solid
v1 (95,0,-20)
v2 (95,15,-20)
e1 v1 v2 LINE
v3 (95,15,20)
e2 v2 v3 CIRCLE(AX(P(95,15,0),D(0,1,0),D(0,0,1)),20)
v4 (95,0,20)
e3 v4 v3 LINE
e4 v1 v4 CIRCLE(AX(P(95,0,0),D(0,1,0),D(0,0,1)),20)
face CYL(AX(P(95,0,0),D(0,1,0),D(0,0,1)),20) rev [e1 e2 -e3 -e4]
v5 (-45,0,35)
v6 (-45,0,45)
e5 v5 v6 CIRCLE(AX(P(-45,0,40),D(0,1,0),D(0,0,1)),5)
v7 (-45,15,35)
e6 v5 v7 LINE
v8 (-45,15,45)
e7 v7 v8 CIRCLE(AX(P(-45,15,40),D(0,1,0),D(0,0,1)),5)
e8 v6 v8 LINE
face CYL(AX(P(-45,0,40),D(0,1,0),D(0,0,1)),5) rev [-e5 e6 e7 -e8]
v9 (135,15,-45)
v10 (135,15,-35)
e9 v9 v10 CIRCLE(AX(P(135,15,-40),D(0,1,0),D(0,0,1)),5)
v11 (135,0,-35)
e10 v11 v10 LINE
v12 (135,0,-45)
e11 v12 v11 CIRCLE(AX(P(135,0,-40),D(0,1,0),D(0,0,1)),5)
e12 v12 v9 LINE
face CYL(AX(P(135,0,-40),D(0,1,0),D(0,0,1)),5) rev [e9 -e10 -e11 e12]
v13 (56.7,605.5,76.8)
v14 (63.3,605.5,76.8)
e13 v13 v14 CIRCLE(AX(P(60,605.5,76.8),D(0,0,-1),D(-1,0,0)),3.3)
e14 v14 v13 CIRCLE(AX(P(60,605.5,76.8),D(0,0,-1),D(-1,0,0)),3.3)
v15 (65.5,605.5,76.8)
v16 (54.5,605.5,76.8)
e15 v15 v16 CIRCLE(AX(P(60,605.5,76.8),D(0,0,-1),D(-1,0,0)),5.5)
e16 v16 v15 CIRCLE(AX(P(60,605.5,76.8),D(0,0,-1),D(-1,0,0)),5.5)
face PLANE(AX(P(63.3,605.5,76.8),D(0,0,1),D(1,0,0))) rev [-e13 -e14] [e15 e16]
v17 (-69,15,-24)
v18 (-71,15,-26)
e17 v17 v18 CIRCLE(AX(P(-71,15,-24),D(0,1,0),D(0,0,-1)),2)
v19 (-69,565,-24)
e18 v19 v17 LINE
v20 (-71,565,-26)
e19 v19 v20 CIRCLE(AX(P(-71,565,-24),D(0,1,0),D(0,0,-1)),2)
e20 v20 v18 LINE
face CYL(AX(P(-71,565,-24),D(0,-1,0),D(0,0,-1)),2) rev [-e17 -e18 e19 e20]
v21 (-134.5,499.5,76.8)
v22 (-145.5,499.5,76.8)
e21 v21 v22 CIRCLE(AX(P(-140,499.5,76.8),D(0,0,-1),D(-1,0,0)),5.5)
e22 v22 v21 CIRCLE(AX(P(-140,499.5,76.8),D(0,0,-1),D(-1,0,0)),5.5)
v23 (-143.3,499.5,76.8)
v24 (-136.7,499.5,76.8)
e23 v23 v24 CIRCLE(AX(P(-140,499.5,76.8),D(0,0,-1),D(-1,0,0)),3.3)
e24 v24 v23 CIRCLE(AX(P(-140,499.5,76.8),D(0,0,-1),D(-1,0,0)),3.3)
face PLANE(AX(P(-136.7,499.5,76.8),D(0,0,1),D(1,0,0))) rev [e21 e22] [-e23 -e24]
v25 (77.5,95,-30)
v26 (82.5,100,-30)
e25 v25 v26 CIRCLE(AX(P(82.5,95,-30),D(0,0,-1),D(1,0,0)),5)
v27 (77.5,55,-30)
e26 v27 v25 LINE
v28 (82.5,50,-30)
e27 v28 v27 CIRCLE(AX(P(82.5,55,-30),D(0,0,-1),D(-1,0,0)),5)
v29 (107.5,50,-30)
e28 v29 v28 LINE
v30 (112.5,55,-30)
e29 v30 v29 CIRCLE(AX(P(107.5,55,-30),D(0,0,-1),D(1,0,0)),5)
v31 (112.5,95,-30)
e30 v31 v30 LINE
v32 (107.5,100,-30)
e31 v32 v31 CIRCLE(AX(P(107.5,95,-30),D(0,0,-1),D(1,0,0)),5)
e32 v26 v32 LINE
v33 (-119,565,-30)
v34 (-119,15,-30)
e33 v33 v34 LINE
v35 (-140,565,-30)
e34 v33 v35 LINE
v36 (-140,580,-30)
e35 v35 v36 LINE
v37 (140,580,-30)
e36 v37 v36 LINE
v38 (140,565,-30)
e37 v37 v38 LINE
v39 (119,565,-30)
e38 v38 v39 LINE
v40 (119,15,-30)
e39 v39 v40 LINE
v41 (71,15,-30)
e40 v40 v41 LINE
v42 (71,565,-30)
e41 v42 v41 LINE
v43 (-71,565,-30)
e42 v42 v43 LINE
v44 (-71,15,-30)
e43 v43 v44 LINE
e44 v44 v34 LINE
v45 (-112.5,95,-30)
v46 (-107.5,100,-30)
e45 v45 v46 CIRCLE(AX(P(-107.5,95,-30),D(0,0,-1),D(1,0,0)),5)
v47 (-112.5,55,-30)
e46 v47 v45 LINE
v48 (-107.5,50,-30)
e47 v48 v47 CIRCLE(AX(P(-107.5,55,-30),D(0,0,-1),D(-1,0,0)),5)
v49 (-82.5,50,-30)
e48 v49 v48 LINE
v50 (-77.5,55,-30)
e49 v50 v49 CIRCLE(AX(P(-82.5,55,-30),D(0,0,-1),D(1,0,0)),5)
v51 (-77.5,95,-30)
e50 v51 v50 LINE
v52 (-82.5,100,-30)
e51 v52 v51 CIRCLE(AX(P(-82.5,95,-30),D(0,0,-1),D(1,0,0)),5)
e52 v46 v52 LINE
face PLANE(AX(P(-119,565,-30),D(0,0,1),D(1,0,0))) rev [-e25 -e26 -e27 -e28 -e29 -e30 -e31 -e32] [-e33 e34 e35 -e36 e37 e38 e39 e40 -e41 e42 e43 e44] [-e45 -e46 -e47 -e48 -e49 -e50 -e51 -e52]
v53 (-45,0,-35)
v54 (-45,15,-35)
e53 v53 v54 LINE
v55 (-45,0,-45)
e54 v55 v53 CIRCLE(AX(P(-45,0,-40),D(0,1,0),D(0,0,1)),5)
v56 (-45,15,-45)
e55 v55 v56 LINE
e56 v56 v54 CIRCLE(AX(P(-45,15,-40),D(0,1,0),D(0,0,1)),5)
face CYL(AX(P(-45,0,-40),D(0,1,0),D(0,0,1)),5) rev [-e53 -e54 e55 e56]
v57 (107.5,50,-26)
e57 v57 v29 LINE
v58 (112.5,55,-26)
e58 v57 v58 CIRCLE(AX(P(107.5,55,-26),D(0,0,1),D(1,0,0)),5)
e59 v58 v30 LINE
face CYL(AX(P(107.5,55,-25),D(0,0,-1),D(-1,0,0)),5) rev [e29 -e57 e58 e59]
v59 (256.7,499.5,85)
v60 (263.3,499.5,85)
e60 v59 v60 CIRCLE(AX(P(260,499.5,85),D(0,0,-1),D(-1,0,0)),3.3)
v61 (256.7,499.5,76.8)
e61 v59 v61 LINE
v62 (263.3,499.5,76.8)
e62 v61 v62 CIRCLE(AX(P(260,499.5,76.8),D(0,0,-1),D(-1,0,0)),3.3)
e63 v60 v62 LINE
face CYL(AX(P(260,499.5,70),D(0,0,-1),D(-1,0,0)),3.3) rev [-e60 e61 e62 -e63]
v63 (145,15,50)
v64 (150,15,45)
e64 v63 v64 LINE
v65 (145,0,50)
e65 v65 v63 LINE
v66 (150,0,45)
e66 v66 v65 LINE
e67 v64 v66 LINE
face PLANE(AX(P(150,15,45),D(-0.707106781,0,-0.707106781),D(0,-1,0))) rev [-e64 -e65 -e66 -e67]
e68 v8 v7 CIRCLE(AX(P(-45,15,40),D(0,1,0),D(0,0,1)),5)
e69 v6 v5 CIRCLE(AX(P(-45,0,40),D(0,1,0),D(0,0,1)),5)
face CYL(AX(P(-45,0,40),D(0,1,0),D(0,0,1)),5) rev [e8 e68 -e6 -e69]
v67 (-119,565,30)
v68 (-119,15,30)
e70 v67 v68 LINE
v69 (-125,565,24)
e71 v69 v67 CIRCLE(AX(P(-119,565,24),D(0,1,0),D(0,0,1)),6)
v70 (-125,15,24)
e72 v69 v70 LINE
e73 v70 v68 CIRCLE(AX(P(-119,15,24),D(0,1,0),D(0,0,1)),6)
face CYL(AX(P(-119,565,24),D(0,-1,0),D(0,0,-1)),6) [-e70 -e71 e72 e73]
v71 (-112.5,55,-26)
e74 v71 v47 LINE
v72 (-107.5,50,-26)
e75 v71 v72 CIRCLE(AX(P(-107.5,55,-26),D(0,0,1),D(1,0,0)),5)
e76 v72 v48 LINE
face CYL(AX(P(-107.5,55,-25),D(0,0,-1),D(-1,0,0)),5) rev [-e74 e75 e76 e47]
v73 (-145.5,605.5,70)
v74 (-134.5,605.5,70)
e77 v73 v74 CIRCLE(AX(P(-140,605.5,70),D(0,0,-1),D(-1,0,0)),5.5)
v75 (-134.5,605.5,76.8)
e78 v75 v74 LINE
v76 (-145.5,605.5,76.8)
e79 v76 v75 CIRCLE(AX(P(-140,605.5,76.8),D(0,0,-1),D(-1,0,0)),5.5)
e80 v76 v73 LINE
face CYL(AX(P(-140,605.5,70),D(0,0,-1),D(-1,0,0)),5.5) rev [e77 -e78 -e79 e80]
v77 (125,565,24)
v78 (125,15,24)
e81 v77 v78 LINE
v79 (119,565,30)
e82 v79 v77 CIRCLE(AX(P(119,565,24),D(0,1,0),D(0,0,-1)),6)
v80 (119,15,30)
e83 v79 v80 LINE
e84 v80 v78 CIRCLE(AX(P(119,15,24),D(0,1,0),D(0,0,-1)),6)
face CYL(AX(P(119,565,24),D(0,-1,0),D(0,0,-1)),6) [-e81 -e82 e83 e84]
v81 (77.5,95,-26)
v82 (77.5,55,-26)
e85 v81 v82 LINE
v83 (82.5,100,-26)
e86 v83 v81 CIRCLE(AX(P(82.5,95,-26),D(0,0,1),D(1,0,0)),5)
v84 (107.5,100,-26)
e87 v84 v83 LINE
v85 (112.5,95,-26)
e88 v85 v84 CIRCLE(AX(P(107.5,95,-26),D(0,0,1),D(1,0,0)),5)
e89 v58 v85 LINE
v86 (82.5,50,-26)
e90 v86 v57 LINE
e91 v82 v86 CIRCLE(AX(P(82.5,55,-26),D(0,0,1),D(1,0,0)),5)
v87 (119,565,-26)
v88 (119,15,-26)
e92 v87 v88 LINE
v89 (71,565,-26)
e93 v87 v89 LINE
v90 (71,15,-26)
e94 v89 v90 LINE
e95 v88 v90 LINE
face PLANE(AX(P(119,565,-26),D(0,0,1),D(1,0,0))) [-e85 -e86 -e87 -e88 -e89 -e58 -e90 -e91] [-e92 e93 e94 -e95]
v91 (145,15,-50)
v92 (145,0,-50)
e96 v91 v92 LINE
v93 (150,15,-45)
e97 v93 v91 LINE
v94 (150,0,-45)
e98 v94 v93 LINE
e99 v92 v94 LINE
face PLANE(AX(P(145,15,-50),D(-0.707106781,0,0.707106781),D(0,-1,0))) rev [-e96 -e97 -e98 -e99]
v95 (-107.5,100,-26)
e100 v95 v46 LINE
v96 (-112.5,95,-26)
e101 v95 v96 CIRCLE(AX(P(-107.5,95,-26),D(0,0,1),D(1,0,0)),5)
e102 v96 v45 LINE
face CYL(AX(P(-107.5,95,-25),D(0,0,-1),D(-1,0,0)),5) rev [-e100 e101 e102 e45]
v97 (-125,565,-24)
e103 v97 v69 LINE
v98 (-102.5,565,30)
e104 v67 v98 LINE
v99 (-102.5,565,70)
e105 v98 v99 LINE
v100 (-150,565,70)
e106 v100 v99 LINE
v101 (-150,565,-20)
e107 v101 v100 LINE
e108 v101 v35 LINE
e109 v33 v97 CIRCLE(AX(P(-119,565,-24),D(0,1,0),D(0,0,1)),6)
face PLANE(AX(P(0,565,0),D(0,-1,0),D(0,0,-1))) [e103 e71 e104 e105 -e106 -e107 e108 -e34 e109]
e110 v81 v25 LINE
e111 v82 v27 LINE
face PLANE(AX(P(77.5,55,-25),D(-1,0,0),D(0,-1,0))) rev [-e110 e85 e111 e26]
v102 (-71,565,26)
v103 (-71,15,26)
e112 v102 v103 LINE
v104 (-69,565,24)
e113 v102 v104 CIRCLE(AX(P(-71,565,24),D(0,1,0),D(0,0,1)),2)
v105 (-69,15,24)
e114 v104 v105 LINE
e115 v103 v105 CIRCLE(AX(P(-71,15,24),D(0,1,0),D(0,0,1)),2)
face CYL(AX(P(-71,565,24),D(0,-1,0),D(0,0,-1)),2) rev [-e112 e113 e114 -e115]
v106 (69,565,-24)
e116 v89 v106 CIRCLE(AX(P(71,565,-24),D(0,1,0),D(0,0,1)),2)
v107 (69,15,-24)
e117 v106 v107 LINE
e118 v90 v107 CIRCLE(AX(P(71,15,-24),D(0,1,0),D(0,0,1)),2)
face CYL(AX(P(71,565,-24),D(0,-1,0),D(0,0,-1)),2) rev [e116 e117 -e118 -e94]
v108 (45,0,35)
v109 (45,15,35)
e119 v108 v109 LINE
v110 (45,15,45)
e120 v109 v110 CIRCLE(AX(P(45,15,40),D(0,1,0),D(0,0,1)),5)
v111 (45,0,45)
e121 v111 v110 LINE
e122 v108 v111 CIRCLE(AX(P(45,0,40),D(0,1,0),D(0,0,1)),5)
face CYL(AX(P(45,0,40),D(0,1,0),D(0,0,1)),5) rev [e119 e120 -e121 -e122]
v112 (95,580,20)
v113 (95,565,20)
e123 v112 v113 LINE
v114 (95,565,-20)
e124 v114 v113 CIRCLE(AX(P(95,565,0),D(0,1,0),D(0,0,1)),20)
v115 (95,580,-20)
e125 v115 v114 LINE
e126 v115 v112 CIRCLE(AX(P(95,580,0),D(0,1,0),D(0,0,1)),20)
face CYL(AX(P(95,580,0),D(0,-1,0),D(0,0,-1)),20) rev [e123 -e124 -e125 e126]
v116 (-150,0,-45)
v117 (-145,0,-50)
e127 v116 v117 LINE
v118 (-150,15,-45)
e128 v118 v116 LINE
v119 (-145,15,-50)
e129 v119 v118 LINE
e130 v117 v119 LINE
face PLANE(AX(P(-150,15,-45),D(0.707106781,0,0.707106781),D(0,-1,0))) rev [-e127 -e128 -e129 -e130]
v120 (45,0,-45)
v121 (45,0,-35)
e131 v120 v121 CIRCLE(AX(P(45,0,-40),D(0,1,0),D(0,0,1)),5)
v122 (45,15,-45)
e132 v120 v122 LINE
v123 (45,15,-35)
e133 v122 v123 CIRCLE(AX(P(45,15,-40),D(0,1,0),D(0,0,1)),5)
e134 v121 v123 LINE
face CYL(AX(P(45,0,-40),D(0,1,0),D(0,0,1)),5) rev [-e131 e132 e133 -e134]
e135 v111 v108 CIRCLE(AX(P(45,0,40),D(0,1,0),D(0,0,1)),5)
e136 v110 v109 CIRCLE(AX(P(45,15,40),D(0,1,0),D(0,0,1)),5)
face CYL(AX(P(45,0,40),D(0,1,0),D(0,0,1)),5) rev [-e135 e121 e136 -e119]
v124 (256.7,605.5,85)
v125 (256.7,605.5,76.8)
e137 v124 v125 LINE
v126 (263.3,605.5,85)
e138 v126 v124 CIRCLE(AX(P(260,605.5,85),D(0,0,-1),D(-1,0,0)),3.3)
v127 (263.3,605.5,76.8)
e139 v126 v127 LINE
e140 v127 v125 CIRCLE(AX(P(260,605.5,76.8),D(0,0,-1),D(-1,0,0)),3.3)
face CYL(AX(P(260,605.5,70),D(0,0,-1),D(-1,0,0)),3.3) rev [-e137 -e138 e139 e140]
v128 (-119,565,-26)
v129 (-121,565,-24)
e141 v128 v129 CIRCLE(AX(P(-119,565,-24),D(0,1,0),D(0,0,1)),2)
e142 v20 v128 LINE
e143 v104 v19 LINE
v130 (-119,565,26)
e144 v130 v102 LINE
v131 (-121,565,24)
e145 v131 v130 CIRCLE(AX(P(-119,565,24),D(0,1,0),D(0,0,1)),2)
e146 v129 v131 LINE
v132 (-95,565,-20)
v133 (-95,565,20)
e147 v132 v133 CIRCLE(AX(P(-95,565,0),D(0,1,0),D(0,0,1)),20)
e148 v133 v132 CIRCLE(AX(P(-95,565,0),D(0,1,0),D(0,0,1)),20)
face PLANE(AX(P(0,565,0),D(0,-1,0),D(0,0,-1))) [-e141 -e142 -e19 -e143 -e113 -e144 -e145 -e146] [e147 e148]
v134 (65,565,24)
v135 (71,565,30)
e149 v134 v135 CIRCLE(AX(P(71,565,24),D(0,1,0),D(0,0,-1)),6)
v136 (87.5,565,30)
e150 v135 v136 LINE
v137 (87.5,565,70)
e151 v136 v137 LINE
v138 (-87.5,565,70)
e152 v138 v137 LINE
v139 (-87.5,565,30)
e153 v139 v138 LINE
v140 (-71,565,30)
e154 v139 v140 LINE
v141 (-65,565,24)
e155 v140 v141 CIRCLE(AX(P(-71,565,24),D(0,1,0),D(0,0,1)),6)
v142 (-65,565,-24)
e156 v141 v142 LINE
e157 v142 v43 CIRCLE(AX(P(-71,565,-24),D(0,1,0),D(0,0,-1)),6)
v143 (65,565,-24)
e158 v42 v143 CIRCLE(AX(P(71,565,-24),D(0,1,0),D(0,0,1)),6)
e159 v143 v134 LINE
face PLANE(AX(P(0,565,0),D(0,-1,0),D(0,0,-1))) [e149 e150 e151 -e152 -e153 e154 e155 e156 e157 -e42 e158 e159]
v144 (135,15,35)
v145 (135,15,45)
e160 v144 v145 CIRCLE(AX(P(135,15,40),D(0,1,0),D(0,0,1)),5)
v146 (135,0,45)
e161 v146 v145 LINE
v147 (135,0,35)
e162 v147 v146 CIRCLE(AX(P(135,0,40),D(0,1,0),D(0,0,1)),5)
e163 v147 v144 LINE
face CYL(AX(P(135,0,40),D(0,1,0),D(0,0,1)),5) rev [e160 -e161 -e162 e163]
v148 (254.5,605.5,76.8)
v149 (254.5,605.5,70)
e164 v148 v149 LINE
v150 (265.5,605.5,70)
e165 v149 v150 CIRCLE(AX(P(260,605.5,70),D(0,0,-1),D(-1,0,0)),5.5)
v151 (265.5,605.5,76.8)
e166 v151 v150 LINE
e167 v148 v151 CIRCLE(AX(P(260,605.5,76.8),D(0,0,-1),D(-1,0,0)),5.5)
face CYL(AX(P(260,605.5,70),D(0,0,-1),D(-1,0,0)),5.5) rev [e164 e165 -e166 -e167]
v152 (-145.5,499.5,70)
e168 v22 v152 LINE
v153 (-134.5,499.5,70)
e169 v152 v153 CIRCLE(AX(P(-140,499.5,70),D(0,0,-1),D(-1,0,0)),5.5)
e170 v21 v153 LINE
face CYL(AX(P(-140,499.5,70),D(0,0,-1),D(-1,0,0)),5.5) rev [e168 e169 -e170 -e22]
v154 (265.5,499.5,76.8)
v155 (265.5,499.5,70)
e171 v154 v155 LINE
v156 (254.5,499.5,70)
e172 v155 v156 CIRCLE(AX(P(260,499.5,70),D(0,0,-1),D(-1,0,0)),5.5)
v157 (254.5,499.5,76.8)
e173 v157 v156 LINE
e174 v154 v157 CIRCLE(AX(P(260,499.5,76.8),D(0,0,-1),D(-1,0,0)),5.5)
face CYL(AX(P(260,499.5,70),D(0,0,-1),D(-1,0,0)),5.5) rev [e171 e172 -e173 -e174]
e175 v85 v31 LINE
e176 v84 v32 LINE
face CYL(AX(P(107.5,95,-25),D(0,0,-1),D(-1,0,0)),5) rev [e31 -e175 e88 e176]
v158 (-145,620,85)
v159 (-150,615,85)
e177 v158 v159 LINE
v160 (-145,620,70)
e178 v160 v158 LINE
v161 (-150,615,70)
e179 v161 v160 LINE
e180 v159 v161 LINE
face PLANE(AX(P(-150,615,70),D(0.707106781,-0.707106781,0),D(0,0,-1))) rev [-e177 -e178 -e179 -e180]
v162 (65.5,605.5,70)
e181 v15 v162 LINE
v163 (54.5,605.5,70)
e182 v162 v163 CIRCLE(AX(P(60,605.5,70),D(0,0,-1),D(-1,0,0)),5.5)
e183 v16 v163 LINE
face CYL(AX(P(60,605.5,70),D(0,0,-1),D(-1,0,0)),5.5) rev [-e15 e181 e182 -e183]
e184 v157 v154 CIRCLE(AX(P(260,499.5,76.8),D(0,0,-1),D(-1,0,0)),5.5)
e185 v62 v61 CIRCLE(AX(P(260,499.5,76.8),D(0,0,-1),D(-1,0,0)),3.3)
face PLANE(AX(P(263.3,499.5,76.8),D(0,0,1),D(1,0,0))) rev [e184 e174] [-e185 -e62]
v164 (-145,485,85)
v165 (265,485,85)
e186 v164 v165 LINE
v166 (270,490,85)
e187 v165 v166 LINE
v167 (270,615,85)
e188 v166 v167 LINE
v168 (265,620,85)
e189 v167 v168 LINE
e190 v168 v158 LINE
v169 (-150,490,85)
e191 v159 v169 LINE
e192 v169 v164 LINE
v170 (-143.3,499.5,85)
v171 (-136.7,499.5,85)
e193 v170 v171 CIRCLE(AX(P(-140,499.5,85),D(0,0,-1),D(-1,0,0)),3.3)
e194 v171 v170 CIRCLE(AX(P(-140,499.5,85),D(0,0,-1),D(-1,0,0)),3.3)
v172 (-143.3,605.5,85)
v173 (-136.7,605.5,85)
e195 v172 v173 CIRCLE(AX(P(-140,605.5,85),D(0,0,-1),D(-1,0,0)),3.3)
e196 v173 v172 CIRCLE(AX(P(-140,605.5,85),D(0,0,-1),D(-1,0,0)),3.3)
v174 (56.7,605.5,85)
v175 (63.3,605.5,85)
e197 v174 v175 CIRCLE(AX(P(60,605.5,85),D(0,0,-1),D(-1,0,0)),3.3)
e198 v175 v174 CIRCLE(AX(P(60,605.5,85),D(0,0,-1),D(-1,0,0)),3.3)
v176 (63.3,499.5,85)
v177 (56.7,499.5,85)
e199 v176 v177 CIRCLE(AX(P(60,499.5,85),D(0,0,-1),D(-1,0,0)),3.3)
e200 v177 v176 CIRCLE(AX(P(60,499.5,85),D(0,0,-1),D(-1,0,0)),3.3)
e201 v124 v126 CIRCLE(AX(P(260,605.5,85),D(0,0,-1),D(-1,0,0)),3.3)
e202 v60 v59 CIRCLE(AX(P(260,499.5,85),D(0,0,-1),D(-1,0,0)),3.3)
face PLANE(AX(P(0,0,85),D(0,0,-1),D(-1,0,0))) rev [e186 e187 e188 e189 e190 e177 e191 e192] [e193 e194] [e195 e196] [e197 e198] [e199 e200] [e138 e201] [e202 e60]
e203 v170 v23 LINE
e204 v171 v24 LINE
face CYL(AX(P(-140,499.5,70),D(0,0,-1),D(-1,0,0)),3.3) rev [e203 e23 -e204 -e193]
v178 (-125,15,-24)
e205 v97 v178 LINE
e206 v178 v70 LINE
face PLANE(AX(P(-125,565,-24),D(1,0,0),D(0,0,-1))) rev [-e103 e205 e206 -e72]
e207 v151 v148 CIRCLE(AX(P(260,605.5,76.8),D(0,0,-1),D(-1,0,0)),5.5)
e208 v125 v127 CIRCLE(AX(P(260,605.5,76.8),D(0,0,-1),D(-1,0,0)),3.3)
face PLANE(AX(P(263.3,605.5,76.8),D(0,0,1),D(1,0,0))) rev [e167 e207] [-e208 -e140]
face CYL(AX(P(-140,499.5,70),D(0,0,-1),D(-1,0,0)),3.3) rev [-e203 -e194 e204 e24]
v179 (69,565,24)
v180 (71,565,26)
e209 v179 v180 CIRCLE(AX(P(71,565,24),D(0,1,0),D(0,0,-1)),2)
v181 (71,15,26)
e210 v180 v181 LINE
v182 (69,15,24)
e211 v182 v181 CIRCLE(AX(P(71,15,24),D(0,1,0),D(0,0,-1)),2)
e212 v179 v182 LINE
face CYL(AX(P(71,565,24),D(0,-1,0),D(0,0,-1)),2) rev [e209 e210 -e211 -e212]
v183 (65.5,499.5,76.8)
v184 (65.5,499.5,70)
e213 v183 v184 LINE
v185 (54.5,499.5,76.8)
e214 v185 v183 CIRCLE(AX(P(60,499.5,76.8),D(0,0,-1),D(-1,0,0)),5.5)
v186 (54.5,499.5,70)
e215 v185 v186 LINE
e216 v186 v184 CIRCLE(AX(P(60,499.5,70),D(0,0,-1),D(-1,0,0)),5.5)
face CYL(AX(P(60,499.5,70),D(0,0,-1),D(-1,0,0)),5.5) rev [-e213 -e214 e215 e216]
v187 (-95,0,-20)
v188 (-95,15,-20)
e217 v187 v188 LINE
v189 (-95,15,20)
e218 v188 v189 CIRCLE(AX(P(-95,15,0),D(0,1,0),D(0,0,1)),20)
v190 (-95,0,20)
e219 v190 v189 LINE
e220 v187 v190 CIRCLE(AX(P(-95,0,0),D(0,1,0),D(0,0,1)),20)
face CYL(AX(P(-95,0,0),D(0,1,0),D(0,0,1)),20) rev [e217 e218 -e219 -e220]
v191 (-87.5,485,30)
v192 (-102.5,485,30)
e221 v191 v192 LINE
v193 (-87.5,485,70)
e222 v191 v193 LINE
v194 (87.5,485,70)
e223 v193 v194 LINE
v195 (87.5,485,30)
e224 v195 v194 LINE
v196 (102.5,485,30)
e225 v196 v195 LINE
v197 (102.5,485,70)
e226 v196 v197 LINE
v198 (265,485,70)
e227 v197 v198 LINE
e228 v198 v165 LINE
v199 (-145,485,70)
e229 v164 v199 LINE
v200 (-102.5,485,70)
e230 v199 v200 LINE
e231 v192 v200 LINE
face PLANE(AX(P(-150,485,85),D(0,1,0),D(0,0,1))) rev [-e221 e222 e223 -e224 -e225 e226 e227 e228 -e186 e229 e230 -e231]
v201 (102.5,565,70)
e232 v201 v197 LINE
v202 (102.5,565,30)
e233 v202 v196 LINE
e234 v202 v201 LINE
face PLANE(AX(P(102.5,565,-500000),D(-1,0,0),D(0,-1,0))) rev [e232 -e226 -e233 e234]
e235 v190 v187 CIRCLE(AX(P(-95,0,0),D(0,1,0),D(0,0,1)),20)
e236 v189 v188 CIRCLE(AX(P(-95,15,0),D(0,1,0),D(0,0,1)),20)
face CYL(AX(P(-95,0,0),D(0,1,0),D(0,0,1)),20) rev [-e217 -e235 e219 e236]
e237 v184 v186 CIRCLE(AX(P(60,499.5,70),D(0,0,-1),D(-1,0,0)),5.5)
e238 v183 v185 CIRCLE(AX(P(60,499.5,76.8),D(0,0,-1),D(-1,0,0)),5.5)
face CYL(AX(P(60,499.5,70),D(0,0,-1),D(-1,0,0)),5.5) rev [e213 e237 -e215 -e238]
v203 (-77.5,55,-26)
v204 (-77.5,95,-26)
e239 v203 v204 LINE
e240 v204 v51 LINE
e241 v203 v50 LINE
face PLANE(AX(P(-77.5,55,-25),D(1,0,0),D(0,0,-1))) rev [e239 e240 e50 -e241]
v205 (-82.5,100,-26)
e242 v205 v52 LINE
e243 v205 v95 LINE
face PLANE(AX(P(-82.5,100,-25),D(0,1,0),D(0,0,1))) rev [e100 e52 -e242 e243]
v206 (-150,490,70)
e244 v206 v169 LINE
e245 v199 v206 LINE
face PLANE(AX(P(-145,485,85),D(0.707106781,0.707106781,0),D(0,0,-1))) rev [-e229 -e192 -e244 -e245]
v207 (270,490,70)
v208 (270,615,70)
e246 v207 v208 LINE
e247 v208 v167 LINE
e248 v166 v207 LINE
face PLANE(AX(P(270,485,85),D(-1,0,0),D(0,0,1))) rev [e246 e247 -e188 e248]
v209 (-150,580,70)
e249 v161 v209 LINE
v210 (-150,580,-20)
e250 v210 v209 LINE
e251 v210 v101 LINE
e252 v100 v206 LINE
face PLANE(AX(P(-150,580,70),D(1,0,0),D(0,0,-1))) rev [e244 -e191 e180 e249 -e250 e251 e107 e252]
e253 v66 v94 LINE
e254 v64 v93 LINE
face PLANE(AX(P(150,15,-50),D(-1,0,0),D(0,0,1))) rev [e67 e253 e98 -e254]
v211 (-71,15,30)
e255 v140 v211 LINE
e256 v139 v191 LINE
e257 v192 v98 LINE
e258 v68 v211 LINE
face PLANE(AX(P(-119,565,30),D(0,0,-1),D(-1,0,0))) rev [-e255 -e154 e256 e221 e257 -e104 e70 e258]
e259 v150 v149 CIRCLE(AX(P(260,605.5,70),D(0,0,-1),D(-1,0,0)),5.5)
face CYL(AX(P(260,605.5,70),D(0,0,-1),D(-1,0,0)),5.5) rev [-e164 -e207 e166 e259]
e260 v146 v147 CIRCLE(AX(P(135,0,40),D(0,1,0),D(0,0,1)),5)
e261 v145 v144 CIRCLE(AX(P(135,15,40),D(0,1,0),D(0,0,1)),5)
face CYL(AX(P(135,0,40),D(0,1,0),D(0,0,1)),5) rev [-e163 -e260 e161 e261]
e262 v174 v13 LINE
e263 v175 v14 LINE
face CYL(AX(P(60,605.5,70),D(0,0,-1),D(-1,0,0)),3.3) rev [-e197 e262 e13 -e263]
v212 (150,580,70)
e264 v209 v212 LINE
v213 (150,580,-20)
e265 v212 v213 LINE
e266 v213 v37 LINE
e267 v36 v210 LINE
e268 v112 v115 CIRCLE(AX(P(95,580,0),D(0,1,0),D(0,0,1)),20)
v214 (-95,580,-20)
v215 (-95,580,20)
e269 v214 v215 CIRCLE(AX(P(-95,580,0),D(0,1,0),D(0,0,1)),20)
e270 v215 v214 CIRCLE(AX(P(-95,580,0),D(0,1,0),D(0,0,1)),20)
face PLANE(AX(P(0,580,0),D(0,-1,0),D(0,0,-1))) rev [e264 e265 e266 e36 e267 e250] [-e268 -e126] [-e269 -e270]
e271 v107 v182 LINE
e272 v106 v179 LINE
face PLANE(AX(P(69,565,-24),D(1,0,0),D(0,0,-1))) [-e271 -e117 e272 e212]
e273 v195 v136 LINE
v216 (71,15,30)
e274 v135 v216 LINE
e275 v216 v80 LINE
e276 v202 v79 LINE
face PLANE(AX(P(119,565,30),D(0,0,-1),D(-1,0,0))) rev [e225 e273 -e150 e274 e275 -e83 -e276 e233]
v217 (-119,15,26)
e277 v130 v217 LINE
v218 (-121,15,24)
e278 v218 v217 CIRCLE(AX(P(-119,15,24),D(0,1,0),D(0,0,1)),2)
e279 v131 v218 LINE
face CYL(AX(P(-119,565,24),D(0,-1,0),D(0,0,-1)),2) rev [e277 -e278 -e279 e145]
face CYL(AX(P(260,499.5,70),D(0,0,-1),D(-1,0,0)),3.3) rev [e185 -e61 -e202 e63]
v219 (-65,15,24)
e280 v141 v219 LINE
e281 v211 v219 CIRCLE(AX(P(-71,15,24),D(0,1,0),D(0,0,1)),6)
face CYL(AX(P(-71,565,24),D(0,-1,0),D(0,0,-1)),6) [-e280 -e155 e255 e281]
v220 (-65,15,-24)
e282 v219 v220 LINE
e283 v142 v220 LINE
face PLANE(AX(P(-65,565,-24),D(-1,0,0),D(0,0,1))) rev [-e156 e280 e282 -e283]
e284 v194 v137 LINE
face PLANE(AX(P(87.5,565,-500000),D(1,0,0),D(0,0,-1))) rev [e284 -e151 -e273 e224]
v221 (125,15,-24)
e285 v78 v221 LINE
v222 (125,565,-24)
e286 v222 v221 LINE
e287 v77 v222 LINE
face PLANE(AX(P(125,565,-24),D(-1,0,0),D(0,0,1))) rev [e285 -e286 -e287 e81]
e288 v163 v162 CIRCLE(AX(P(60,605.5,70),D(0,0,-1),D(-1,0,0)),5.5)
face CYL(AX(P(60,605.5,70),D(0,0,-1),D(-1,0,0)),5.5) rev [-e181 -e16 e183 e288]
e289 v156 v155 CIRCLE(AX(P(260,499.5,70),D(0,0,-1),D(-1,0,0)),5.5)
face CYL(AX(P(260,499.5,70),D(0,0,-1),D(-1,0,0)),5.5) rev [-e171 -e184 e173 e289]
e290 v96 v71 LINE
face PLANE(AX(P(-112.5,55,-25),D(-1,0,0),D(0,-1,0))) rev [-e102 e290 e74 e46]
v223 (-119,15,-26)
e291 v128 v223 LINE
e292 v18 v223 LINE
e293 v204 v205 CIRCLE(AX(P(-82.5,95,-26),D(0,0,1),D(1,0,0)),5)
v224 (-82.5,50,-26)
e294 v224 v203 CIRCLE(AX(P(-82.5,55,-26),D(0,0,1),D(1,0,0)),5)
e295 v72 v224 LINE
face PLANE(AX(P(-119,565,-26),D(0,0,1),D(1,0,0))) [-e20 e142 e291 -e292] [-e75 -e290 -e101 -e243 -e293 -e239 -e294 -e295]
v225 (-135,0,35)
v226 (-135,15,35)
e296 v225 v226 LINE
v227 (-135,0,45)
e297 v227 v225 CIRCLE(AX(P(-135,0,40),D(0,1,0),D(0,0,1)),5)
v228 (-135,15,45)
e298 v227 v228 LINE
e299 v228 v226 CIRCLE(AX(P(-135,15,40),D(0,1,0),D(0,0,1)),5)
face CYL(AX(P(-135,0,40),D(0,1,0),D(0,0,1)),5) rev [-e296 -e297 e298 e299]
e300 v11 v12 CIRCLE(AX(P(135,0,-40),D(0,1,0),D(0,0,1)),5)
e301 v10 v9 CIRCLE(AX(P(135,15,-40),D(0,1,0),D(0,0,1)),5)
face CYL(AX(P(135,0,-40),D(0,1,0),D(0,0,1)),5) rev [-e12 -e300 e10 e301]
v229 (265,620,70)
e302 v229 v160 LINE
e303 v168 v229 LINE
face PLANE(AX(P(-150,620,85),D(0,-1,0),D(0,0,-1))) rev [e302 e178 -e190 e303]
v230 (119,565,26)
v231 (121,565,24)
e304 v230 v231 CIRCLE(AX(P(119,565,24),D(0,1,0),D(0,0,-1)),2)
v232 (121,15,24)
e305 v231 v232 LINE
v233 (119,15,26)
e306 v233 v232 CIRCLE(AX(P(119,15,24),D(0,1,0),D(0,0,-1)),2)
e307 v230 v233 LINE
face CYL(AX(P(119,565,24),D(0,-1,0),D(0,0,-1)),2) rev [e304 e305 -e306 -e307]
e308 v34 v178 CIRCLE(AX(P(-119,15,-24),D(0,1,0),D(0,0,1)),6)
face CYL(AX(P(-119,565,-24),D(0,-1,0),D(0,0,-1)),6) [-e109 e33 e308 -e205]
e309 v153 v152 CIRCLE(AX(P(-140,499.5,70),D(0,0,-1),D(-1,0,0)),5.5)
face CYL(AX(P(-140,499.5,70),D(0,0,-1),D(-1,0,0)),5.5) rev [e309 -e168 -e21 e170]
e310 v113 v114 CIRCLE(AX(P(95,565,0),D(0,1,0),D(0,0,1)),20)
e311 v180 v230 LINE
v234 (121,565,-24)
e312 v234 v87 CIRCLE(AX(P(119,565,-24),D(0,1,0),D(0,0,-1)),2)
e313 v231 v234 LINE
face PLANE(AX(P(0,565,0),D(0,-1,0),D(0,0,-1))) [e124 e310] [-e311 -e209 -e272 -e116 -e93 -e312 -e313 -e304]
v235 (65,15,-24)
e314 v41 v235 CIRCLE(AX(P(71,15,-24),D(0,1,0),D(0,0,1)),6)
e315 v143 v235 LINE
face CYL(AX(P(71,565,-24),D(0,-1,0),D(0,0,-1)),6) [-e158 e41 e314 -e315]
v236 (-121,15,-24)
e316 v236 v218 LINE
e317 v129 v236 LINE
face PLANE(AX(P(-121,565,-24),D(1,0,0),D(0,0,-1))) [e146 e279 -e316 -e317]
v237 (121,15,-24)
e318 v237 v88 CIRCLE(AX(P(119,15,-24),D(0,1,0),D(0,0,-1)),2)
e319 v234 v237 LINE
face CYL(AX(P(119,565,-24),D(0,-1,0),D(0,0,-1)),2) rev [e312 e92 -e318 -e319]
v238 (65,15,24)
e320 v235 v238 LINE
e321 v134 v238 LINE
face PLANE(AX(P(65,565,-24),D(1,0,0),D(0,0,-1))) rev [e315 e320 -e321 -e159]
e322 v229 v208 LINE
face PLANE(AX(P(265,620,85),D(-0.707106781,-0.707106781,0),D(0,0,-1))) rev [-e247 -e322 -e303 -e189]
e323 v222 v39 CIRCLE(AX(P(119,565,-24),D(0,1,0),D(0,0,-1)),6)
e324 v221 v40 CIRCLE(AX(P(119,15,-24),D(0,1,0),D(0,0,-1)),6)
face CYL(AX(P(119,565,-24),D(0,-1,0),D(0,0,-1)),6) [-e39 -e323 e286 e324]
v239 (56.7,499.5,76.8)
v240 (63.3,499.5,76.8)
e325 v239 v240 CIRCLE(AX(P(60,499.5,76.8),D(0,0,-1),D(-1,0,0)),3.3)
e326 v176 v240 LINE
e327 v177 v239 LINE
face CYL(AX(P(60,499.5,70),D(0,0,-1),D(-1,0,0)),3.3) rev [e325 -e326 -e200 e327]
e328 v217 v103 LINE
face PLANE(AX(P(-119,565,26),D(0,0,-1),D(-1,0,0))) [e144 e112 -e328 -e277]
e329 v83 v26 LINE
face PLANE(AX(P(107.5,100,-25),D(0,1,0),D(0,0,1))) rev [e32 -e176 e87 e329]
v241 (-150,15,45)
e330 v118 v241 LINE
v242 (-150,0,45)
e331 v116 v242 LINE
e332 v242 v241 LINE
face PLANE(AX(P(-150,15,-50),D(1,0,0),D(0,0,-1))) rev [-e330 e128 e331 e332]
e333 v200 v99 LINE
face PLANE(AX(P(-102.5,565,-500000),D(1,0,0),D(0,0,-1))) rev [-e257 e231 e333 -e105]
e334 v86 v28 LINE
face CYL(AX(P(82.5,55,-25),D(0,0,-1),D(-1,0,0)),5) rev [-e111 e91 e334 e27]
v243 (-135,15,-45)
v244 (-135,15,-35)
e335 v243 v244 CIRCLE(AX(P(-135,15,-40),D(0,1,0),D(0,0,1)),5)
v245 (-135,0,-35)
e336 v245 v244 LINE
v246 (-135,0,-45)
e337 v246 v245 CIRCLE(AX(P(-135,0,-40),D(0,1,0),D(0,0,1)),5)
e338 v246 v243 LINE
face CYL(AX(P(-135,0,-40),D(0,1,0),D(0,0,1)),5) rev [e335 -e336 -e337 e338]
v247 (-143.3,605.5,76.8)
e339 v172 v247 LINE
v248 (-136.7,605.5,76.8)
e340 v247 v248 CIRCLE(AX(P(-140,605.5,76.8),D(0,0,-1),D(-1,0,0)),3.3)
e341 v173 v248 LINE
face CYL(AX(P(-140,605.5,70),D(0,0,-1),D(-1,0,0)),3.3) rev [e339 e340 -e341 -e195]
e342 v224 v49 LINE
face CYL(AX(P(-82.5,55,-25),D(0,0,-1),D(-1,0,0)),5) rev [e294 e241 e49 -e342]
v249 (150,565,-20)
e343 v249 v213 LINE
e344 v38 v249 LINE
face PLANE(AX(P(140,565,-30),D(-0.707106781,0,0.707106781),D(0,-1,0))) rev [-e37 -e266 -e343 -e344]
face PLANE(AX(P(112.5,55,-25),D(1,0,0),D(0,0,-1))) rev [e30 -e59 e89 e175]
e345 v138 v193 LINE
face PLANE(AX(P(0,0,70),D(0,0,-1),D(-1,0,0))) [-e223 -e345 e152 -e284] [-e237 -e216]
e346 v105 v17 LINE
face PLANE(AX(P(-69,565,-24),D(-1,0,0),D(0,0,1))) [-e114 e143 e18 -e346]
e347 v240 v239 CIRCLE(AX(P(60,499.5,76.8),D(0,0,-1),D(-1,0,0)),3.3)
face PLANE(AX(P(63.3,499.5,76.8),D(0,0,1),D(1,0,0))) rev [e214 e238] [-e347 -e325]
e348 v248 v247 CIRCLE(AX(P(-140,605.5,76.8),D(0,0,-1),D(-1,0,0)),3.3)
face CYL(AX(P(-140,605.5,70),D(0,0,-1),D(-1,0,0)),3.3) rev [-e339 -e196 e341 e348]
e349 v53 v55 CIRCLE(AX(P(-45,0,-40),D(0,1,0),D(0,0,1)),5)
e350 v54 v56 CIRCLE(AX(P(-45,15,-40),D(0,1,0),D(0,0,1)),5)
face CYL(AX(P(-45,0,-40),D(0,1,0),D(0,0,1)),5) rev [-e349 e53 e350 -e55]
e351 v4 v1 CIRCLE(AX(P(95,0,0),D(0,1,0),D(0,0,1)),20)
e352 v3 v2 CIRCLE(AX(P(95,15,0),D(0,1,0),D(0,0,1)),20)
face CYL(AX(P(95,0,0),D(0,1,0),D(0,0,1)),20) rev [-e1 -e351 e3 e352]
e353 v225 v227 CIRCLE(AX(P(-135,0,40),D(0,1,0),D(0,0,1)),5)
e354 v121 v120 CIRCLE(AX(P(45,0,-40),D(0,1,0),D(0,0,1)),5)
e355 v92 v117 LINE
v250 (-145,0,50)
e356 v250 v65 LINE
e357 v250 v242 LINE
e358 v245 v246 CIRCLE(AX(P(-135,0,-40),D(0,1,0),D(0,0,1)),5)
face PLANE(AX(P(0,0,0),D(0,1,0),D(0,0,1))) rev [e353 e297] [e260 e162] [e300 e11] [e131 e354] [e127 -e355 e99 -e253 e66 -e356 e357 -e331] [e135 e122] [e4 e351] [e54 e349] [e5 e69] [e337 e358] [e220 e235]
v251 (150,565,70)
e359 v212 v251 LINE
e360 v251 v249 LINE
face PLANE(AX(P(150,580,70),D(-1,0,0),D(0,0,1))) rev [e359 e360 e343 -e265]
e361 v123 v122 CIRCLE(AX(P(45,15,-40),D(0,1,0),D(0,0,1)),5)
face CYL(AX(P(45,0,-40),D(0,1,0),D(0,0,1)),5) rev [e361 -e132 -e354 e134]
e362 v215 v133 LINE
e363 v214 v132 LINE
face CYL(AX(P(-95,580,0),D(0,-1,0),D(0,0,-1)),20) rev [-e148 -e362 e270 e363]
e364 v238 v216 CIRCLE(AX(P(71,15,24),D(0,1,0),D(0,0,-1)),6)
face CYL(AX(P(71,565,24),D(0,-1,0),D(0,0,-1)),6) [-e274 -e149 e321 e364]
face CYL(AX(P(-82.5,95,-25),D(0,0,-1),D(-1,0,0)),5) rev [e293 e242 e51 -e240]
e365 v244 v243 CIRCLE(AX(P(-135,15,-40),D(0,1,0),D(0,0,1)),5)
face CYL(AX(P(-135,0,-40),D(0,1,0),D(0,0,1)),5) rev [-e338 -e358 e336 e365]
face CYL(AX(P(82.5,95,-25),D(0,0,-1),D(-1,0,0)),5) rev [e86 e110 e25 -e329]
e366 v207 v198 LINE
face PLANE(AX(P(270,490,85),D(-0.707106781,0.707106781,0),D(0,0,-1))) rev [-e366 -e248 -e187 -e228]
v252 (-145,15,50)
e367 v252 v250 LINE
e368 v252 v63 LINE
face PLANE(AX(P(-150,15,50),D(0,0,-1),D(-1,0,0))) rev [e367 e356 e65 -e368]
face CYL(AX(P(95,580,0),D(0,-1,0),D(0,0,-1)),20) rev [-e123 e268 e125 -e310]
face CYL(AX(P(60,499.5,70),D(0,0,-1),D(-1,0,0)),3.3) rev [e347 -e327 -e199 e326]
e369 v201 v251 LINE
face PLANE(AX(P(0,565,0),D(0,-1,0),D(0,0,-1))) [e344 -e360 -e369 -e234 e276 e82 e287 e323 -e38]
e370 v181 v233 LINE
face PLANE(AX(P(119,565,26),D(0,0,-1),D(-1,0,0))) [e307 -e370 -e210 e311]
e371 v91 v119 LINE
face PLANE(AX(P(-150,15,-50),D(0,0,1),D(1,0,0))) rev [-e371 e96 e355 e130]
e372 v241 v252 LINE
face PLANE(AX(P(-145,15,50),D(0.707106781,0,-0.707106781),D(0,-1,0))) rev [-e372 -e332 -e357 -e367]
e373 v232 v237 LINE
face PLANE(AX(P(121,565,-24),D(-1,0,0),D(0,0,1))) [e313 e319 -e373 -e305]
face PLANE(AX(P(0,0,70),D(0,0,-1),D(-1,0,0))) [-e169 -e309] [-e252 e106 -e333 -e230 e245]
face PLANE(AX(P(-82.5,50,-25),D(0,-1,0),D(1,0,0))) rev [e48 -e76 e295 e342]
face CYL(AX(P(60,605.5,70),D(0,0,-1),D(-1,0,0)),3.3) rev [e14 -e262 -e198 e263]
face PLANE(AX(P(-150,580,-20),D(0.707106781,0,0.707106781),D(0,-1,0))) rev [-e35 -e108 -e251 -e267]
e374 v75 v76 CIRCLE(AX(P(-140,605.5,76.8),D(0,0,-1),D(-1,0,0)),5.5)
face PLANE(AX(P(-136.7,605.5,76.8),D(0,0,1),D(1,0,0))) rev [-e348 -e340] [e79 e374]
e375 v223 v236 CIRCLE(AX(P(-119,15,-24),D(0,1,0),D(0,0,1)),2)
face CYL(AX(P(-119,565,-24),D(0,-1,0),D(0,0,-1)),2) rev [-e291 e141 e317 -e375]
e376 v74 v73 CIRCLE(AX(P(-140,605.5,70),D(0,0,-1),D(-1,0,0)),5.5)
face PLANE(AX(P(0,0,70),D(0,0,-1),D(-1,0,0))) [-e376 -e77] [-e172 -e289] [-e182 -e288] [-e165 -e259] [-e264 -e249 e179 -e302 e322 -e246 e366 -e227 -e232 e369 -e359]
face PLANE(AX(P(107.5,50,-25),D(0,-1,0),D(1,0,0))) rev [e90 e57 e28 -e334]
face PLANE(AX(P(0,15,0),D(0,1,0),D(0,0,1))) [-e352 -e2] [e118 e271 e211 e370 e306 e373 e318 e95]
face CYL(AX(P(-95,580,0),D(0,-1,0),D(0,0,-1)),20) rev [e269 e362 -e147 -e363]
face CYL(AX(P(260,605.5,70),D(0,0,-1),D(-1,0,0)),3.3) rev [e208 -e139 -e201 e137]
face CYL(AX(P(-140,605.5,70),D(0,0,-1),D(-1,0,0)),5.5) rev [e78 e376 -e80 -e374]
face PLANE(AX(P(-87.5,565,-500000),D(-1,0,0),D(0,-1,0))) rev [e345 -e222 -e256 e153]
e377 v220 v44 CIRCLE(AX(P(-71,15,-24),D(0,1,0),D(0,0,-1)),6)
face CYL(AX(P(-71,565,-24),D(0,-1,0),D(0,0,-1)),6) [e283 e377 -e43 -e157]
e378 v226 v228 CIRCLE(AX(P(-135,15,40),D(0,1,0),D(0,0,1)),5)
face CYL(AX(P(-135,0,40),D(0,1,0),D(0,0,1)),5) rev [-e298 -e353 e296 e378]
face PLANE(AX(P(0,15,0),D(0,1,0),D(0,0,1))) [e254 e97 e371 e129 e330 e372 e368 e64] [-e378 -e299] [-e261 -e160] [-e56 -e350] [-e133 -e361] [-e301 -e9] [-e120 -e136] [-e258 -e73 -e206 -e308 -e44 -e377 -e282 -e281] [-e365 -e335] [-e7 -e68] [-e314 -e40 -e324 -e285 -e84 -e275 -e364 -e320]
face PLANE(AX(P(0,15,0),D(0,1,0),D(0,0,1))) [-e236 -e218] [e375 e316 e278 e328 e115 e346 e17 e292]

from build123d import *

# Parameters (mm, degrees)
SKETCH_1_W                  = 300
SKETCH_1_H                  = 100
EXTRUDE_1_DEPTH             = 15
EXTRUDE_2_DEPTH             = 550
SKETCH_3_W                  = 300
SKETCH_3_H                  = 100
SKETCH_3_R                  = 20
EXTRUDE_3_DEPTH             = 15
SKETCH_4_W                  = 420
SKETCH_4_H                  = 135
EXTRUDE_4_DEPTH             = 15
HOLE_WIZARD_1_AT_2_COUNT    = 2
HOLE_WIZARD_1_AT_2_PITCH    = 106
PATTERN_LINEAR_1_COUNT      = 3
PATTERN_LINEAR_1_PITCH      = 200
SKETCH_7_R                  = 20
CUT_EXTRUDE_1_DEPTH         = 668.944608482
CHAMFER_1_SIZE              = 10
CHAMFER_2_SIZE              = 5
EXTRUDE_5_REACH             = 688.804
SKETCH_8_W                  = 15
SKETCH_8_H                  = 80
SKETCH_9_R                  = 5
CUT_EXTRUDE_2_DEPTH         = 668.944608482
PATTERN_LINEAR_2_COUNT      = 4
PATTERN_LINEAR_2_PITCH      = 90
PATTERN_LINEAR_2_COUNT_DIR2 = 2
PATTERN_LINEAR_2_PITCH_DIR2 = 80
CHAMFER_3_SIZE              = 5
CUT_EXTRUDE_3_DEPTH         = 5


with BuildPart() as part:
    # 草图1 → 凸台-拉伸1 (new body)
    with BuildSketch(Plane(origin=(0, 0, 0), x_dir=(1, 0, 0), z_dir=(0, 1, 0))):
        Rectangle(SKETCH_1_W, SKETCH_1_H)
    extrude(amount=EXTRUDE_1_DEPTH)

    # 草图2 → 凸台-拉伸2 (add)
    # profile 1 of 2: a face of its own
    with BuildSketch(Plane(origin=(0, 15, 0), x_dir=(1, 0, 0), z_dir=(0, 1, 0))):
        with BuildLine():
            Line((-119, 30), (-71, 30))
            ThreePointArc((-71, 30), (-66.757359313, 28.242640687), (-65, 24))
            Line((-65, 24), (-65, -24))
            ThreePointArc((-65, -24), (-66.757359313, -28.242640687), (-71, -30))
            Line((-71, -30), (-119, -30))
            ThreePointArc((-119, -30), (-123.242640687, -28.242640687), (-125, -24))
            Line((-125, -24), (-125, 24))
            ThreePointArc((-125, 24), (-123.242640687, 28.242640687), (-119, 30))
        make_face()
        with BuildLine():
            Line((-119, 26), (-71, 26))
            ThreePointArc((-71, 26), (-69.585786438, 25.414213562), (-69, 24))
            Line((-69, 24), (-69, -24))
            ThreePointArc((-69, -24), (-69.585786438, -25.414213562), (-71, -26))
            Line((-71, -26), (-119, -26))
            ThreePointArc((-119, -26), (-120.414213562, -25.414213562), (-121, -24))
            Line((-121, -24), (-121, 24))
            ThreePointArc((-121, 24), (-120.414213562, 25.414213562), (-119, 26))
        make_face(mode=Mode.SUBTRACT)
    # profile 2 of 2: a face of its own
    with BuildSketch(Plane(origin=(0, 15, 0), x_dir=(1, 0, 0), z_dir=(0, 1, 0))):
        with BuildLine():
            Line((65, 24), (65, -24))
            ThreePointArc((65, -24), (66.757359313, -28.242640687), (71, -30))
            Line((71, -30), (119, -30))
            ThreePointArc((119, -30), (123.242640687, -28.242640687), (125, -24))
            Line((125, -24), (125, 24))
            ThreePointArc((125, 24), (123.242640687, 28.242640687), (119, 30))
            Line((119, 30), (71, 30))
            ThreePointArc((71, 30), (66.757359313, 28.242640687), (65, 24))
        make_face()
        with BuildLine():
            Line((121, 24), (121, -24))
            ThreePointArc((121, -24), (120.414213562, -25.414213562), (119, -26))
            Line((119, -26), (71, -26))
            ThreePointArc((71, -26), (69.585786438, -25.414213562), (69, -24))
            Line((69, -24), (69, 24))
            ThreePointArc((69, 24), (69.585786438, 25.414213562), (71, 26))
            Line((71, 26), (119, 26))
            ThreePointArc((119, 26), (120.414213562, 25.414213562), (121, 24))
        make_face(mode=Mode.SUBTRACT)
    extrude(amount=EXTRUDE_2_DEPTH)

    # 草图3 → 凸台-拉伸3 (add)
    with BuildSketch(Plane(origin=(0, 565, 0), x_dir=(1, 0, 0), z_dir=(0, 1, 0))):
        with Locations((0, -20)):
            Rectangle(SKETCH_3_W, SKETCH_3_H)
        with Locations(Location((-95, 0, 0), (0, 0, 270))):
            Circle(SKETCH_3_R, mode=Mode.SUBTRACT)
        with Locations(Location((95, 0, 0), (0, 0, 270))):
            Circle(SKETCH_3_R, mode=Mode.SUBTRACT)
    extrude(amount=EXTRUDE_3_DEPTH)

    # 草图4 → 凸台-拉伸4 (add)
    with BuildSketch(Plane.XY.offset(70)):
        with Locations((60, 552.5)):
            Rectangle(SKETCH_4_W, SKETCH_4_H)
    extrude(amount=EXTRUDE_4_DEPTH)

    # 草图5 → 打孔尺寸(%根据)内六角圆柱头螺钉的类型1 (revolve, cut)
    with BuildSketch(Plane(origin=(-140, 605.5, 70), x_dir=(0, 1, 0), z_dir=(1, 0, 0))):
        Polygon((0, 0), (0, 16.982840043), (3.3, 15), (3.3, 6.8), (5.5, 6.8), (5.5, 0), align=None)
    hole_wizard_1 = revolve(axis=Axis((-140, 605.5, 63.65), (0, 0, 1)), mode=Mode.SUBTRACT)

    # 打孔尺寸(%根据)内六角圆柱头螺钉的类型1 at 2: 打孔尺寸(%根据)内六角圆柱头螺钉的类型1 ×2
    with Locations(*[(0, -i * HOLE_WIZARD_1_AT_2_PITCH, 0) for i in range(1, HOLE_WIZARD_1_AT_2_COUNT)]):
        add(hole_wizard_1, mode=Mode.SUBTRACT)

    # 阵列(线性)1: 打孔尺寸(%根据)内六角圆柱头螺钉的类型1 ×3
    with Locations(*[(i * PATTERN_LINEAR_1_PITCH, 0, 0) for i in range(1, PATTERN_LINEAR_1_COUNT)]):
        add(hole_wizard_1, mode=Mode.SUBTRACT)

    # 阵列(线性)1 copy 1 sketch → 阵列(线性)1 copy 1 (revolve, cut)
    with BuildSketch(Plane(origin=(60, 499.5, 70), x_dir=(0, 1, 0), z_dir=(1, 0, 0))):
        Polygon((0, 0), (0, 16.982840043), (3.3, 15), (3.3, 6.8), (5.5, 6.8), (5.5, 0), align=None)
    revolve(axis=Axis((60, 499.5, 63.65), (0, 0, 1)), mode=Mode.SUBTRACT)

    # 阵列(线性)1 copy 2 sketch → 阵列(线性)1 copy 2 (revolve, cut)
    with BuildSketch(Plane(origin=(260, 499.5, 70), x_dir=(0, 1, 0), z_dir=(1, 0, 0))):
        Polygon((0, 0), (0, 16.982840043), (3.3, 15), (3.3, 6.8), (5.5, 6.8), (5.5, 0), align=None)
    revolve(axis=Axis((260, 499.5, 63.65), (0, 0, 1)), mode=Mode.SUBTRACT)

    # 草图7 → 切除-拉伸1 (cut, through all)
    with BuildSketch(Plane(origin=(0, 15, 0), x_dir=(1, 0, 0), z_dir=(0, 1, 0))):
        with Locations(Location((-95, 0, 0), (0, 0, 270))):
            Circle(SKETCH_7_R)
        with Locations(Location((95, 0, 0), (0, 0, 270))):
            Circle(SKETCH_7_R)
    extrude(amount=-CUT_EXTRUDE_1_DEPTH, mode=Mode.SUBTRACT)

    # 倒角1
    chamfer_1_edges = [part.edges().sort_by_distance(p)[0] for p in [
        (-150, 572.5, -30),
        (150, 572.5, -30),
    ]]
    chamfer(chamfer_1_edges, length=CHAMFER_1_SIZE)

    # 倒角2
    chamfer_2_edges = [part.edges().sort_by_distance(p)[0] for p in [
        (270, 485, 77.5),
        (270, 620, 77.5),
        (-150, 485, 77.5),
        (-150, 620, 77.5),
    ]]
    chamfer(chamfer_2_edges, length=CHAMFER_2_SIZE)

    # 草图8 → 凸台-拉伸5 (add, up to next)
    with BuildSketch(Plane(origin=(0, 0, 70), x_dir=(-1, 0, 0), z_dir=(0, 0, -1)), mode=Mode.PRIVATE) as extrude_5_sk1:
        with Locations((-95, 525)):
            Rectangle(SKETCH_8_W, SKETCH_8_H)
    extrude_5_tool1 = extrude(extrude_5_sk1.sketch, amount=EXTRUDE_5_REACH, mode=Mode.PRIVATE) - part.part
    # 草图8 → 凸台-拉伸5 (add, up to next)
    with BuildSketch(Plane(origin=(0, 0, 70), x_dir=(-1, 0, 0), z_dir=(0, 0, -1)), mode=Mode.PRIVATE) as extrude_5_sk2:
        with Locations((95, 525)):
            Rectangle(SKETCH_8_W, SKETCH_8_H)
    extrude_5_tool2 = extrude(extrude_5_sk2.sketch, amount=EXTRUDE_5_REACH, mode=Mode.PRIVATE) - part.part
    add(extrude_5_tool1.solids().sort_by_distance((95, 525, 70))[0])
    add(extrude_5_tool2.solids().sort_by_distance((-95, 525, 70))[0])

    # 草图9 → 切除-拉伸2 (cut, through all)
    with BuildSketch(Plane(origin=(0, 15, 0), x_dir=(1, 0, 0), z_dir=(0, 1, 0))):
        with Locations(Location((-135, 40, 0), (0, 0, 270))):
            Circle(SKETCH_9_R)
    cut_extrude_2 = extrude(amount=-CUT_EXTRUDE_2_DEPTH, mode=Mode.SUBTRACT)

    # 阵列(线性)2: Cut-Extrude 2 4 × 2
    with Locations(*[(i * PATTERN_LINEAR_2_PITCH, 0, j * PATTERN_LINEAR_2_PITCH_DIR2) for i in range(PATTERN_LINEAR_2_COUNT) for j in range(PATTERN_LINEAR_2_COUNT_DIR2) if (i, j) != (0, 0)]):
        add(cut_extrude_2, mode=Mode.SUBTRACT)

    # 倒角3
    chamfer_3_edges = [part.edges().sort_by_distance(p)[0] for p in [
        (150, 7.5, 50),
        (-150, 7.5, 50),
        (-150, 7.5, -50),
        (150, 7.5, -50),
    ]]
    chamfer(chamfer_3_edges, length=CHAMFER_3_SIZE)

    # 草图10 → 切除-拉伸3 (cut)
    with BuildSketch(Plane(origin=(0, 0, -30), x_dir=(-1, 0, 0), z_dir=(0, 0, -1))):
        with BuildLine():
            Line((-107.5, 50), (-82.5, 50))
            ThreePointArc((-82.5, 50), (-78.964466094, 51.464466094), (-77.5, 55))
            Line((-77.5, 55), (-77.5, 95))
            ThreePointArc((-77.5, 95), (-78.964466094, 98.535533906), (-82.5, 100))
            Line((-82.5, 100), (-107.5, 100))
            ThreePointArc((-107.5, 100), (-111.035533906, 98.535533906), (-112.5, 95))
            Line((-112.5, 95), (-112.5, 55))
            ThreePointArc((-112.5, 55), (-111.035533906, 51.464466094), (-107.5, 50))
        make_face()
        with BuildLine():
            Line((82.5, 50), (107.5, 50))
            ThreePointArc((107.5, 50), (111.035533906, 51.464466094), (112.5, 55))
            Line((112.5, 55), (112.5, 95))
            ThreePointArc((112.5, 95), (111.035533906, 98.535533906), (107.5, 100))
            Line((107.5, 100), (82.5, 100))
            ThreePointArc((82.5, 100), (78.964466094, 98.535533906), (77.5, 95))
            Line((77.5, 95), (77.5, 55))
            ThreePointArc((77.5, 55), (78.964466094, 51.464466094), (82.5, 50))
        make_face()
    extrude(amount=-CUT_EXTRUDE_3_DEPTH, mode=Mode.SUBTRACT)


solid = part.part
